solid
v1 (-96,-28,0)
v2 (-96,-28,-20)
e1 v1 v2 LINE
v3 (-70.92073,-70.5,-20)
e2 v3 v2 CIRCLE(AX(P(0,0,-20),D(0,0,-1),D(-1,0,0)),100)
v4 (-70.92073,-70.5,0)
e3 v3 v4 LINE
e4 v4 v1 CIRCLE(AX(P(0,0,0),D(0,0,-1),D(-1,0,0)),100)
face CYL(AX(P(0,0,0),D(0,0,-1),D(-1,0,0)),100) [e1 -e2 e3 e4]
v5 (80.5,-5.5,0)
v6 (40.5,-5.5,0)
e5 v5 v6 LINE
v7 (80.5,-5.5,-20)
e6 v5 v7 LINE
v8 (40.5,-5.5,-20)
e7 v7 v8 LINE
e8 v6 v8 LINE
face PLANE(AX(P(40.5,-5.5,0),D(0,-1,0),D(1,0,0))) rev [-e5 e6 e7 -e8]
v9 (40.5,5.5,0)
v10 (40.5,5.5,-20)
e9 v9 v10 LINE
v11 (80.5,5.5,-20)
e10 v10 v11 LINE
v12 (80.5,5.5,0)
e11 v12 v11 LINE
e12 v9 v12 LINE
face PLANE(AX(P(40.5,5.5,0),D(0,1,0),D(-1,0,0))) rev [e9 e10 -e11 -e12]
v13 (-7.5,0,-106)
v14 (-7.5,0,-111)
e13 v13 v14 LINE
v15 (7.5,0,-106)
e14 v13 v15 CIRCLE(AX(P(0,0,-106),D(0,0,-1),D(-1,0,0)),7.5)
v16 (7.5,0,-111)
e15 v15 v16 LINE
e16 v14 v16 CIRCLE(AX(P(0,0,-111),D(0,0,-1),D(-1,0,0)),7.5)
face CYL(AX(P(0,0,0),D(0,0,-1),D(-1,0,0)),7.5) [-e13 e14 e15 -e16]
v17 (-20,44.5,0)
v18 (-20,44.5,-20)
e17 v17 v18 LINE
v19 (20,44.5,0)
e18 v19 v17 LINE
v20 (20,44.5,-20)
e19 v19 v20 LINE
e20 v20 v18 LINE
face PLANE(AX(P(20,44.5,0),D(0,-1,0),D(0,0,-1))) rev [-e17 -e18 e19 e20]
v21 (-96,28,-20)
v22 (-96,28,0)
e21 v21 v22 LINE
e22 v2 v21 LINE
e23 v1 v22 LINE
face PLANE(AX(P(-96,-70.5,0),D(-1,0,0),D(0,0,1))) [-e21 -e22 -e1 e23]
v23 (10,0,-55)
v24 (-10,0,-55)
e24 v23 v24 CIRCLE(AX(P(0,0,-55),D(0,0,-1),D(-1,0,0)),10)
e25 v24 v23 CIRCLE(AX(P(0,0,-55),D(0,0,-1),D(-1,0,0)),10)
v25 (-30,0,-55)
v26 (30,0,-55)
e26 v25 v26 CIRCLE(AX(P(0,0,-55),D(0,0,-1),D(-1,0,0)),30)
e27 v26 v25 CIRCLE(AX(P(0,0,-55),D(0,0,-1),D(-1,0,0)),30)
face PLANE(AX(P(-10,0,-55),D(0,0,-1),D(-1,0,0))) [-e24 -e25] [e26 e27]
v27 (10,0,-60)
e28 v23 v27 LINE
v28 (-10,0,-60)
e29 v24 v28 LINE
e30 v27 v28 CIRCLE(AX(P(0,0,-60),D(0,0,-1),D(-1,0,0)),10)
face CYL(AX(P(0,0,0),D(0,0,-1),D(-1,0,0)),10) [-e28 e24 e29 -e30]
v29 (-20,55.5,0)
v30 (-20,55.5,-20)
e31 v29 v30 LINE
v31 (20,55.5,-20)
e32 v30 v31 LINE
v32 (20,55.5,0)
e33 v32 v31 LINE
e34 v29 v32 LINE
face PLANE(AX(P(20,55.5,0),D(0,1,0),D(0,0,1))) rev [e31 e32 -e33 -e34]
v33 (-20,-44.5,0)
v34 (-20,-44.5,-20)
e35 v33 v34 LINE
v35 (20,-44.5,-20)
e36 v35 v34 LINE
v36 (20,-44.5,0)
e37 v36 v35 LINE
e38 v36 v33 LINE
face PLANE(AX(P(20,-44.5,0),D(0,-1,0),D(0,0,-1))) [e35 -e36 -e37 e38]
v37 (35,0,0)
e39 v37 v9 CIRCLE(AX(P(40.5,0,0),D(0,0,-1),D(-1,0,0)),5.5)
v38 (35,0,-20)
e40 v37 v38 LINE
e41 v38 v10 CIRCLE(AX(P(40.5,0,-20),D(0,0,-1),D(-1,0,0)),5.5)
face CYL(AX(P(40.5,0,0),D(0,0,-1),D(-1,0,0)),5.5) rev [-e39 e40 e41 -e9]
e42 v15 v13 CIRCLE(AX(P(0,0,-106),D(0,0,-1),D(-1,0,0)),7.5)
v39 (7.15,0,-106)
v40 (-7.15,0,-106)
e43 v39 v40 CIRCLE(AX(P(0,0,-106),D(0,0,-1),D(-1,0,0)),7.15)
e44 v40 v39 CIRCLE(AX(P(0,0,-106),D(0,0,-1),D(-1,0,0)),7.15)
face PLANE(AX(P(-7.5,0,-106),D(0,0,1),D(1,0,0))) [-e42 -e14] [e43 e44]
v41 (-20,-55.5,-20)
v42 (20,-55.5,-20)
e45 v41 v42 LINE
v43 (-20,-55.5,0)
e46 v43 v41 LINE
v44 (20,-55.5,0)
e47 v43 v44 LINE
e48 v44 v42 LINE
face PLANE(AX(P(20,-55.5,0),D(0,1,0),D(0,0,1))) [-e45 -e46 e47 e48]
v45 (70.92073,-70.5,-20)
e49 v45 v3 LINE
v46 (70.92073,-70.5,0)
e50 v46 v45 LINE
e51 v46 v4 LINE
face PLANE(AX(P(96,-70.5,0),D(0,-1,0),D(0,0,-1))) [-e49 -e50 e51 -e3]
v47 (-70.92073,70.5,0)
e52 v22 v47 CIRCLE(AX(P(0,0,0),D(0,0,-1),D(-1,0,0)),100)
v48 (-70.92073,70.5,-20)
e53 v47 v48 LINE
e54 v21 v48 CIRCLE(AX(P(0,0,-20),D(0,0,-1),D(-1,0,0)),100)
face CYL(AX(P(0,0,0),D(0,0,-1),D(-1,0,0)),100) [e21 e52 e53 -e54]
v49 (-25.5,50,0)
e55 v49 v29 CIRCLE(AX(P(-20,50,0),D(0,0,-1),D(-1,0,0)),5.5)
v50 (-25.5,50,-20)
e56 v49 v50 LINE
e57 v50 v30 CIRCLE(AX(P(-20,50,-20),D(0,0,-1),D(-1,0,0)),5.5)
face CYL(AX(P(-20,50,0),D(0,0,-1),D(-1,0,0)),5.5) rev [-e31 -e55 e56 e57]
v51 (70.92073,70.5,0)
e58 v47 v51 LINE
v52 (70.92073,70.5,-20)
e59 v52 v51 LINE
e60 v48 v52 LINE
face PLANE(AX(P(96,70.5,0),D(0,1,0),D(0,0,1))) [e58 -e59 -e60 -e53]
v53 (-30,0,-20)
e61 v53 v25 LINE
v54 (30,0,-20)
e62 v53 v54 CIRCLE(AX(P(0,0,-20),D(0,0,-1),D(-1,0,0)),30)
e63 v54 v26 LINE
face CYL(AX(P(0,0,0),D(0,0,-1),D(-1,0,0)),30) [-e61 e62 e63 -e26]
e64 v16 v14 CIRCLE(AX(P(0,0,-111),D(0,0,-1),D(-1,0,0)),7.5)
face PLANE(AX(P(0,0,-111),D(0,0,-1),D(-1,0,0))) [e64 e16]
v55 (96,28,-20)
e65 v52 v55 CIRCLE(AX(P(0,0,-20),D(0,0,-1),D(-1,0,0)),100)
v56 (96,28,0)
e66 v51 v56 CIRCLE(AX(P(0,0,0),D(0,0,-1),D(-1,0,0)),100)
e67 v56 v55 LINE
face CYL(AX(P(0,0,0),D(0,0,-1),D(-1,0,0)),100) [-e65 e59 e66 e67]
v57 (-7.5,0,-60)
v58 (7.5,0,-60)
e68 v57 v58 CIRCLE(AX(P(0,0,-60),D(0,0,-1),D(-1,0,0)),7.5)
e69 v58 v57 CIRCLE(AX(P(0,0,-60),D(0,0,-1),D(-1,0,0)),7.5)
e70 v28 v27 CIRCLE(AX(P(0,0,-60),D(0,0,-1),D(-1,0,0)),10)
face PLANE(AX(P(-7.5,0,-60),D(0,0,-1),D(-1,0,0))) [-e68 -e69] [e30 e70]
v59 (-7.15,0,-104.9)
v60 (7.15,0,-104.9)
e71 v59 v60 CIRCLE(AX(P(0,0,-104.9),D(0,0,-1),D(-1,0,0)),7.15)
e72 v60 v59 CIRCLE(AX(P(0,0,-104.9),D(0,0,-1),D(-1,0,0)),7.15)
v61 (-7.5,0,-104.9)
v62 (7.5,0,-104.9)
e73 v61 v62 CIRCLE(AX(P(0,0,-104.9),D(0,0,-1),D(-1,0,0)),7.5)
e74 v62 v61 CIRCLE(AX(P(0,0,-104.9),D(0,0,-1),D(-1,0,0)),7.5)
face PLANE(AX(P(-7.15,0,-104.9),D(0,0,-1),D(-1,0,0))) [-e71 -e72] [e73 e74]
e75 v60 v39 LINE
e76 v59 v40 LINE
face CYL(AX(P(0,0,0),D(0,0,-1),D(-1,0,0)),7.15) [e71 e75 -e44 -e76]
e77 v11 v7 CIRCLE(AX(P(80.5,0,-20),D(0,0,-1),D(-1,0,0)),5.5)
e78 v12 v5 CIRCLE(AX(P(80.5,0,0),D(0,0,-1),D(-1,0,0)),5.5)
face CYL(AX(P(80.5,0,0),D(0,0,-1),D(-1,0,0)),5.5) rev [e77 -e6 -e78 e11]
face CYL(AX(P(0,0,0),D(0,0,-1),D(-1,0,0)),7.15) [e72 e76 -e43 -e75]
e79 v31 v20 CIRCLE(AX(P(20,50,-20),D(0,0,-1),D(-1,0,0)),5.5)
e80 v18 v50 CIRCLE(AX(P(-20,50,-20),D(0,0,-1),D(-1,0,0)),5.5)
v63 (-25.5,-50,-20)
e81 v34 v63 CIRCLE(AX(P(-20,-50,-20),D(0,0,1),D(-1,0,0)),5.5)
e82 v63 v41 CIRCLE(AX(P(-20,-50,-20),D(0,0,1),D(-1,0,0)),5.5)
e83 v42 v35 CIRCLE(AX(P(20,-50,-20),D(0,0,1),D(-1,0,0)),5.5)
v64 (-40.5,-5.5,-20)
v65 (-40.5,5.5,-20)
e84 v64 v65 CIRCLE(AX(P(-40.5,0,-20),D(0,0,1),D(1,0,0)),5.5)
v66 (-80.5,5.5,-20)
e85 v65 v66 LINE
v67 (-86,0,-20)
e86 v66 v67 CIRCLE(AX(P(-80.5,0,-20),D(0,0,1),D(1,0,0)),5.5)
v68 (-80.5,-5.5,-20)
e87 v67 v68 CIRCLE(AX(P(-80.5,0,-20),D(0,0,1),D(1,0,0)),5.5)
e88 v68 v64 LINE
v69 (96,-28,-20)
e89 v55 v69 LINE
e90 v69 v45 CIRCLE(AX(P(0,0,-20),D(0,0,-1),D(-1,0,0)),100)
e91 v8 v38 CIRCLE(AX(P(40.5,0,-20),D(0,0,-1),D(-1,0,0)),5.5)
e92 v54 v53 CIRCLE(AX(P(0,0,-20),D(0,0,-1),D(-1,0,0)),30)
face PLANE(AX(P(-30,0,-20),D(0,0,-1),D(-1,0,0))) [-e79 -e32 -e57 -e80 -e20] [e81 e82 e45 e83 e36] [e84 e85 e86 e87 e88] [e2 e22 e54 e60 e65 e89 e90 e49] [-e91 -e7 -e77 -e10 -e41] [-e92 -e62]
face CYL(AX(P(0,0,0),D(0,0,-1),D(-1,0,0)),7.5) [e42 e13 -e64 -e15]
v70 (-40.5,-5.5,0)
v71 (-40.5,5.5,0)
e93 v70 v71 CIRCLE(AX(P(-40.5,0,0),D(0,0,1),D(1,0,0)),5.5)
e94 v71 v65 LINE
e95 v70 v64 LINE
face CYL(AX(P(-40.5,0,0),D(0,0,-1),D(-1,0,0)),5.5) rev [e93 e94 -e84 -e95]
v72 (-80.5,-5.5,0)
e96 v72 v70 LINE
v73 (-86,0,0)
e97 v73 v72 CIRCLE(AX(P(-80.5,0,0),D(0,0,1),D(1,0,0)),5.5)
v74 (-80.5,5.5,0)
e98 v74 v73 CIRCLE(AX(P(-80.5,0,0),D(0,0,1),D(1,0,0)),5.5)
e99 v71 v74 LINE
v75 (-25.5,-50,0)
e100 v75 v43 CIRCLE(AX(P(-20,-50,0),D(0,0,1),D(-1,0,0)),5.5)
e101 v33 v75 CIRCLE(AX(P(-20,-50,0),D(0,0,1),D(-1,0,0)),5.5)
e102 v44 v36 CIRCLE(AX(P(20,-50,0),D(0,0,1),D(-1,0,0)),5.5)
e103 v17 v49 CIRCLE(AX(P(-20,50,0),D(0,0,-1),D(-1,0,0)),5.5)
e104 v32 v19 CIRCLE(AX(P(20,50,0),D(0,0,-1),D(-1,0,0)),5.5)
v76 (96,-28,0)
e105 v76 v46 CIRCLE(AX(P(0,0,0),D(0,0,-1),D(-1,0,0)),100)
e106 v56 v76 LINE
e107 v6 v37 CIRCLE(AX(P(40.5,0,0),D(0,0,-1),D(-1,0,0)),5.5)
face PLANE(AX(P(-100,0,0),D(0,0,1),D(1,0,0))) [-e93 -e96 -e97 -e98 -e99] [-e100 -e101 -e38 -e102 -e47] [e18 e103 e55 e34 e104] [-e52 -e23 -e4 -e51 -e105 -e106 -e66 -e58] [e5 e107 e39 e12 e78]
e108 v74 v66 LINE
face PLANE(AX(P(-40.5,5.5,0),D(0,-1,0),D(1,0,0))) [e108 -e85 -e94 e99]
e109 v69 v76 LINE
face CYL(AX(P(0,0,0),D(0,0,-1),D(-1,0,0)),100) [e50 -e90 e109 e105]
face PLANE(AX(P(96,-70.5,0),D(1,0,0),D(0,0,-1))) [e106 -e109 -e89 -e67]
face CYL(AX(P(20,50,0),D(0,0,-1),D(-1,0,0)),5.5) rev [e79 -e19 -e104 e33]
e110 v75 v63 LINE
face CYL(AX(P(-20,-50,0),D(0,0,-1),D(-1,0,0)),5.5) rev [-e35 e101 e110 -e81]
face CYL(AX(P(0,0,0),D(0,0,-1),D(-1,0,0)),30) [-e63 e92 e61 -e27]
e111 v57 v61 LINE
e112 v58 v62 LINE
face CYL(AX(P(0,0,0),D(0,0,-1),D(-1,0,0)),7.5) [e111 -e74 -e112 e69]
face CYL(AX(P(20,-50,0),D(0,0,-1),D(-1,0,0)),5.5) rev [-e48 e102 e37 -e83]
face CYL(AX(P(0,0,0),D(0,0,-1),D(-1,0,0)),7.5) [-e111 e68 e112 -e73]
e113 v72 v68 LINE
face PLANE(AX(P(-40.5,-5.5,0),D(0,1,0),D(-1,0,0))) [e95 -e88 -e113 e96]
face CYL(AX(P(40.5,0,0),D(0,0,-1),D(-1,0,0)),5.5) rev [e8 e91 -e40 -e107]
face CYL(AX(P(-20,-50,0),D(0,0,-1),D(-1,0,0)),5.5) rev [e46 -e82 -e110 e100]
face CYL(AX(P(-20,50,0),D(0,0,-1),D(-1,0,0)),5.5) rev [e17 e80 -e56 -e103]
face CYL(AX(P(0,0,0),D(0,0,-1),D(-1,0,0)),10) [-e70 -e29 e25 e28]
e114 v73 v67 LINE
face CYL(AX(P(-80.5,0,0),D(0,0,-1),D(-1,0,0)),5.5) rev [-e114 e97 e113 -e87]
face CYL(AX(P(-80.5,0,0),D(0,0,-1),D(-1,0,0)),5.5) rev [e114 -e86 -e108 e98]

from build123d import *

# Parameters (mm, degrees)
CUT_EXTRUDE_1_DEPTH  = 169.169557293
SKETCH_4_OUTSIDE_W   = 262.768
SKETCH_4_OUTSIDE_H   = 262.768
SKETCH_4_OUTSIDE_W_2 = 192
SKETCH_4_OUTSIDE_H_2 = 141
CUT_EXTRUDE_2_DEPTH  = 169.169557293


with BuildPart() as part:
    # 草图1 → 旋转1 (revolve)
    with BuildSketch(Plane(origin=(0, 0, 0), x_dir=(1, 0, 0), z_dir=(0, 1, 0))):
        Polygon((0, 111), (-7.5, 111), (-7.5, 106), (-7.15, 106), (-7.15, 104.9), (-7.5, 104.9), (-7.5, 60), (-10, 60), (-10, 55), (-30, 55), (-30, 20), (-100, 20), (-100, 0), (0, 0), align=None)
    revolve(axis=Axis((0, 0, 0), (0, 0, 1)))

    # 草图3 → 切除-拉伸1 (cut, through all)
    with BuildSketch(Plane(origin=(0, 0, -20), x_dir=(-1, 0, 0), z_dir=(0, 0, -1))):
        with BuildLine():
            Line((-20, 55.5), (20, 55.5))
            ThreePointArc((20, 55.5), (25.5, 50), (20, 44.5))
            Line((20, 44.5), (-20, 44.5))
            ThreePointArc((-20, 44.5), (-25.5, 50), (-20, 55.5))
        make_face()
        with BuildLine():
            Line((-40.5, -5.5), (-80.5, -5.5))
            ThreePointArc((-80.5, -5.5), (-86, 0), (-80.5, 5.5))
            Line((-80.5, 5.5), (-40.5, 5.5))
            ThreePointArc((-40.5, 5.5), (-35, 0), (-40.5, -5.5))
        make_face()
    cut_extrude_1 = extrude(amount=-CUT_EXTRUDE_1_DEPTH, mode=Mode.SUBTRACT)

    # 镜向1: 切除-拉伸1 across plane
    add(cut_extrude_1.mirror(Plane(origin=(0, 0, 0), x_dir=(0, 0, 1), z_dir=(1, 0, 0))), mode=Mode.SUBTRACT)

    # 镜向2: 切除-拉伸1 across plane
    add(cut_extrude_1.mirror(Plane.ZX), mode=Mode.SUBTRACT)

    # 草图4 outside → 切除-拉伸2 (cut, through all)
    with BuildSketch(Plane(origin=(0, 0, -20), x_dir=(-1, 0, 0), z_dir=(0, 0, -1))):
        Rectangle(SKETCH_4_OUTSIDE_W, SKETCH_4_OUTSIDE_H)
        Rectangle(SKETCH_4_OUTSIDE_W_2, SKETCH_4_OUTSIDE_H_2, mode=Mode.SUBTRACT)
    extrude(amount=-CUT_EXTRUDE_2_DEPTH, mode=Mode.SUBTRACT)


solid = part.part
